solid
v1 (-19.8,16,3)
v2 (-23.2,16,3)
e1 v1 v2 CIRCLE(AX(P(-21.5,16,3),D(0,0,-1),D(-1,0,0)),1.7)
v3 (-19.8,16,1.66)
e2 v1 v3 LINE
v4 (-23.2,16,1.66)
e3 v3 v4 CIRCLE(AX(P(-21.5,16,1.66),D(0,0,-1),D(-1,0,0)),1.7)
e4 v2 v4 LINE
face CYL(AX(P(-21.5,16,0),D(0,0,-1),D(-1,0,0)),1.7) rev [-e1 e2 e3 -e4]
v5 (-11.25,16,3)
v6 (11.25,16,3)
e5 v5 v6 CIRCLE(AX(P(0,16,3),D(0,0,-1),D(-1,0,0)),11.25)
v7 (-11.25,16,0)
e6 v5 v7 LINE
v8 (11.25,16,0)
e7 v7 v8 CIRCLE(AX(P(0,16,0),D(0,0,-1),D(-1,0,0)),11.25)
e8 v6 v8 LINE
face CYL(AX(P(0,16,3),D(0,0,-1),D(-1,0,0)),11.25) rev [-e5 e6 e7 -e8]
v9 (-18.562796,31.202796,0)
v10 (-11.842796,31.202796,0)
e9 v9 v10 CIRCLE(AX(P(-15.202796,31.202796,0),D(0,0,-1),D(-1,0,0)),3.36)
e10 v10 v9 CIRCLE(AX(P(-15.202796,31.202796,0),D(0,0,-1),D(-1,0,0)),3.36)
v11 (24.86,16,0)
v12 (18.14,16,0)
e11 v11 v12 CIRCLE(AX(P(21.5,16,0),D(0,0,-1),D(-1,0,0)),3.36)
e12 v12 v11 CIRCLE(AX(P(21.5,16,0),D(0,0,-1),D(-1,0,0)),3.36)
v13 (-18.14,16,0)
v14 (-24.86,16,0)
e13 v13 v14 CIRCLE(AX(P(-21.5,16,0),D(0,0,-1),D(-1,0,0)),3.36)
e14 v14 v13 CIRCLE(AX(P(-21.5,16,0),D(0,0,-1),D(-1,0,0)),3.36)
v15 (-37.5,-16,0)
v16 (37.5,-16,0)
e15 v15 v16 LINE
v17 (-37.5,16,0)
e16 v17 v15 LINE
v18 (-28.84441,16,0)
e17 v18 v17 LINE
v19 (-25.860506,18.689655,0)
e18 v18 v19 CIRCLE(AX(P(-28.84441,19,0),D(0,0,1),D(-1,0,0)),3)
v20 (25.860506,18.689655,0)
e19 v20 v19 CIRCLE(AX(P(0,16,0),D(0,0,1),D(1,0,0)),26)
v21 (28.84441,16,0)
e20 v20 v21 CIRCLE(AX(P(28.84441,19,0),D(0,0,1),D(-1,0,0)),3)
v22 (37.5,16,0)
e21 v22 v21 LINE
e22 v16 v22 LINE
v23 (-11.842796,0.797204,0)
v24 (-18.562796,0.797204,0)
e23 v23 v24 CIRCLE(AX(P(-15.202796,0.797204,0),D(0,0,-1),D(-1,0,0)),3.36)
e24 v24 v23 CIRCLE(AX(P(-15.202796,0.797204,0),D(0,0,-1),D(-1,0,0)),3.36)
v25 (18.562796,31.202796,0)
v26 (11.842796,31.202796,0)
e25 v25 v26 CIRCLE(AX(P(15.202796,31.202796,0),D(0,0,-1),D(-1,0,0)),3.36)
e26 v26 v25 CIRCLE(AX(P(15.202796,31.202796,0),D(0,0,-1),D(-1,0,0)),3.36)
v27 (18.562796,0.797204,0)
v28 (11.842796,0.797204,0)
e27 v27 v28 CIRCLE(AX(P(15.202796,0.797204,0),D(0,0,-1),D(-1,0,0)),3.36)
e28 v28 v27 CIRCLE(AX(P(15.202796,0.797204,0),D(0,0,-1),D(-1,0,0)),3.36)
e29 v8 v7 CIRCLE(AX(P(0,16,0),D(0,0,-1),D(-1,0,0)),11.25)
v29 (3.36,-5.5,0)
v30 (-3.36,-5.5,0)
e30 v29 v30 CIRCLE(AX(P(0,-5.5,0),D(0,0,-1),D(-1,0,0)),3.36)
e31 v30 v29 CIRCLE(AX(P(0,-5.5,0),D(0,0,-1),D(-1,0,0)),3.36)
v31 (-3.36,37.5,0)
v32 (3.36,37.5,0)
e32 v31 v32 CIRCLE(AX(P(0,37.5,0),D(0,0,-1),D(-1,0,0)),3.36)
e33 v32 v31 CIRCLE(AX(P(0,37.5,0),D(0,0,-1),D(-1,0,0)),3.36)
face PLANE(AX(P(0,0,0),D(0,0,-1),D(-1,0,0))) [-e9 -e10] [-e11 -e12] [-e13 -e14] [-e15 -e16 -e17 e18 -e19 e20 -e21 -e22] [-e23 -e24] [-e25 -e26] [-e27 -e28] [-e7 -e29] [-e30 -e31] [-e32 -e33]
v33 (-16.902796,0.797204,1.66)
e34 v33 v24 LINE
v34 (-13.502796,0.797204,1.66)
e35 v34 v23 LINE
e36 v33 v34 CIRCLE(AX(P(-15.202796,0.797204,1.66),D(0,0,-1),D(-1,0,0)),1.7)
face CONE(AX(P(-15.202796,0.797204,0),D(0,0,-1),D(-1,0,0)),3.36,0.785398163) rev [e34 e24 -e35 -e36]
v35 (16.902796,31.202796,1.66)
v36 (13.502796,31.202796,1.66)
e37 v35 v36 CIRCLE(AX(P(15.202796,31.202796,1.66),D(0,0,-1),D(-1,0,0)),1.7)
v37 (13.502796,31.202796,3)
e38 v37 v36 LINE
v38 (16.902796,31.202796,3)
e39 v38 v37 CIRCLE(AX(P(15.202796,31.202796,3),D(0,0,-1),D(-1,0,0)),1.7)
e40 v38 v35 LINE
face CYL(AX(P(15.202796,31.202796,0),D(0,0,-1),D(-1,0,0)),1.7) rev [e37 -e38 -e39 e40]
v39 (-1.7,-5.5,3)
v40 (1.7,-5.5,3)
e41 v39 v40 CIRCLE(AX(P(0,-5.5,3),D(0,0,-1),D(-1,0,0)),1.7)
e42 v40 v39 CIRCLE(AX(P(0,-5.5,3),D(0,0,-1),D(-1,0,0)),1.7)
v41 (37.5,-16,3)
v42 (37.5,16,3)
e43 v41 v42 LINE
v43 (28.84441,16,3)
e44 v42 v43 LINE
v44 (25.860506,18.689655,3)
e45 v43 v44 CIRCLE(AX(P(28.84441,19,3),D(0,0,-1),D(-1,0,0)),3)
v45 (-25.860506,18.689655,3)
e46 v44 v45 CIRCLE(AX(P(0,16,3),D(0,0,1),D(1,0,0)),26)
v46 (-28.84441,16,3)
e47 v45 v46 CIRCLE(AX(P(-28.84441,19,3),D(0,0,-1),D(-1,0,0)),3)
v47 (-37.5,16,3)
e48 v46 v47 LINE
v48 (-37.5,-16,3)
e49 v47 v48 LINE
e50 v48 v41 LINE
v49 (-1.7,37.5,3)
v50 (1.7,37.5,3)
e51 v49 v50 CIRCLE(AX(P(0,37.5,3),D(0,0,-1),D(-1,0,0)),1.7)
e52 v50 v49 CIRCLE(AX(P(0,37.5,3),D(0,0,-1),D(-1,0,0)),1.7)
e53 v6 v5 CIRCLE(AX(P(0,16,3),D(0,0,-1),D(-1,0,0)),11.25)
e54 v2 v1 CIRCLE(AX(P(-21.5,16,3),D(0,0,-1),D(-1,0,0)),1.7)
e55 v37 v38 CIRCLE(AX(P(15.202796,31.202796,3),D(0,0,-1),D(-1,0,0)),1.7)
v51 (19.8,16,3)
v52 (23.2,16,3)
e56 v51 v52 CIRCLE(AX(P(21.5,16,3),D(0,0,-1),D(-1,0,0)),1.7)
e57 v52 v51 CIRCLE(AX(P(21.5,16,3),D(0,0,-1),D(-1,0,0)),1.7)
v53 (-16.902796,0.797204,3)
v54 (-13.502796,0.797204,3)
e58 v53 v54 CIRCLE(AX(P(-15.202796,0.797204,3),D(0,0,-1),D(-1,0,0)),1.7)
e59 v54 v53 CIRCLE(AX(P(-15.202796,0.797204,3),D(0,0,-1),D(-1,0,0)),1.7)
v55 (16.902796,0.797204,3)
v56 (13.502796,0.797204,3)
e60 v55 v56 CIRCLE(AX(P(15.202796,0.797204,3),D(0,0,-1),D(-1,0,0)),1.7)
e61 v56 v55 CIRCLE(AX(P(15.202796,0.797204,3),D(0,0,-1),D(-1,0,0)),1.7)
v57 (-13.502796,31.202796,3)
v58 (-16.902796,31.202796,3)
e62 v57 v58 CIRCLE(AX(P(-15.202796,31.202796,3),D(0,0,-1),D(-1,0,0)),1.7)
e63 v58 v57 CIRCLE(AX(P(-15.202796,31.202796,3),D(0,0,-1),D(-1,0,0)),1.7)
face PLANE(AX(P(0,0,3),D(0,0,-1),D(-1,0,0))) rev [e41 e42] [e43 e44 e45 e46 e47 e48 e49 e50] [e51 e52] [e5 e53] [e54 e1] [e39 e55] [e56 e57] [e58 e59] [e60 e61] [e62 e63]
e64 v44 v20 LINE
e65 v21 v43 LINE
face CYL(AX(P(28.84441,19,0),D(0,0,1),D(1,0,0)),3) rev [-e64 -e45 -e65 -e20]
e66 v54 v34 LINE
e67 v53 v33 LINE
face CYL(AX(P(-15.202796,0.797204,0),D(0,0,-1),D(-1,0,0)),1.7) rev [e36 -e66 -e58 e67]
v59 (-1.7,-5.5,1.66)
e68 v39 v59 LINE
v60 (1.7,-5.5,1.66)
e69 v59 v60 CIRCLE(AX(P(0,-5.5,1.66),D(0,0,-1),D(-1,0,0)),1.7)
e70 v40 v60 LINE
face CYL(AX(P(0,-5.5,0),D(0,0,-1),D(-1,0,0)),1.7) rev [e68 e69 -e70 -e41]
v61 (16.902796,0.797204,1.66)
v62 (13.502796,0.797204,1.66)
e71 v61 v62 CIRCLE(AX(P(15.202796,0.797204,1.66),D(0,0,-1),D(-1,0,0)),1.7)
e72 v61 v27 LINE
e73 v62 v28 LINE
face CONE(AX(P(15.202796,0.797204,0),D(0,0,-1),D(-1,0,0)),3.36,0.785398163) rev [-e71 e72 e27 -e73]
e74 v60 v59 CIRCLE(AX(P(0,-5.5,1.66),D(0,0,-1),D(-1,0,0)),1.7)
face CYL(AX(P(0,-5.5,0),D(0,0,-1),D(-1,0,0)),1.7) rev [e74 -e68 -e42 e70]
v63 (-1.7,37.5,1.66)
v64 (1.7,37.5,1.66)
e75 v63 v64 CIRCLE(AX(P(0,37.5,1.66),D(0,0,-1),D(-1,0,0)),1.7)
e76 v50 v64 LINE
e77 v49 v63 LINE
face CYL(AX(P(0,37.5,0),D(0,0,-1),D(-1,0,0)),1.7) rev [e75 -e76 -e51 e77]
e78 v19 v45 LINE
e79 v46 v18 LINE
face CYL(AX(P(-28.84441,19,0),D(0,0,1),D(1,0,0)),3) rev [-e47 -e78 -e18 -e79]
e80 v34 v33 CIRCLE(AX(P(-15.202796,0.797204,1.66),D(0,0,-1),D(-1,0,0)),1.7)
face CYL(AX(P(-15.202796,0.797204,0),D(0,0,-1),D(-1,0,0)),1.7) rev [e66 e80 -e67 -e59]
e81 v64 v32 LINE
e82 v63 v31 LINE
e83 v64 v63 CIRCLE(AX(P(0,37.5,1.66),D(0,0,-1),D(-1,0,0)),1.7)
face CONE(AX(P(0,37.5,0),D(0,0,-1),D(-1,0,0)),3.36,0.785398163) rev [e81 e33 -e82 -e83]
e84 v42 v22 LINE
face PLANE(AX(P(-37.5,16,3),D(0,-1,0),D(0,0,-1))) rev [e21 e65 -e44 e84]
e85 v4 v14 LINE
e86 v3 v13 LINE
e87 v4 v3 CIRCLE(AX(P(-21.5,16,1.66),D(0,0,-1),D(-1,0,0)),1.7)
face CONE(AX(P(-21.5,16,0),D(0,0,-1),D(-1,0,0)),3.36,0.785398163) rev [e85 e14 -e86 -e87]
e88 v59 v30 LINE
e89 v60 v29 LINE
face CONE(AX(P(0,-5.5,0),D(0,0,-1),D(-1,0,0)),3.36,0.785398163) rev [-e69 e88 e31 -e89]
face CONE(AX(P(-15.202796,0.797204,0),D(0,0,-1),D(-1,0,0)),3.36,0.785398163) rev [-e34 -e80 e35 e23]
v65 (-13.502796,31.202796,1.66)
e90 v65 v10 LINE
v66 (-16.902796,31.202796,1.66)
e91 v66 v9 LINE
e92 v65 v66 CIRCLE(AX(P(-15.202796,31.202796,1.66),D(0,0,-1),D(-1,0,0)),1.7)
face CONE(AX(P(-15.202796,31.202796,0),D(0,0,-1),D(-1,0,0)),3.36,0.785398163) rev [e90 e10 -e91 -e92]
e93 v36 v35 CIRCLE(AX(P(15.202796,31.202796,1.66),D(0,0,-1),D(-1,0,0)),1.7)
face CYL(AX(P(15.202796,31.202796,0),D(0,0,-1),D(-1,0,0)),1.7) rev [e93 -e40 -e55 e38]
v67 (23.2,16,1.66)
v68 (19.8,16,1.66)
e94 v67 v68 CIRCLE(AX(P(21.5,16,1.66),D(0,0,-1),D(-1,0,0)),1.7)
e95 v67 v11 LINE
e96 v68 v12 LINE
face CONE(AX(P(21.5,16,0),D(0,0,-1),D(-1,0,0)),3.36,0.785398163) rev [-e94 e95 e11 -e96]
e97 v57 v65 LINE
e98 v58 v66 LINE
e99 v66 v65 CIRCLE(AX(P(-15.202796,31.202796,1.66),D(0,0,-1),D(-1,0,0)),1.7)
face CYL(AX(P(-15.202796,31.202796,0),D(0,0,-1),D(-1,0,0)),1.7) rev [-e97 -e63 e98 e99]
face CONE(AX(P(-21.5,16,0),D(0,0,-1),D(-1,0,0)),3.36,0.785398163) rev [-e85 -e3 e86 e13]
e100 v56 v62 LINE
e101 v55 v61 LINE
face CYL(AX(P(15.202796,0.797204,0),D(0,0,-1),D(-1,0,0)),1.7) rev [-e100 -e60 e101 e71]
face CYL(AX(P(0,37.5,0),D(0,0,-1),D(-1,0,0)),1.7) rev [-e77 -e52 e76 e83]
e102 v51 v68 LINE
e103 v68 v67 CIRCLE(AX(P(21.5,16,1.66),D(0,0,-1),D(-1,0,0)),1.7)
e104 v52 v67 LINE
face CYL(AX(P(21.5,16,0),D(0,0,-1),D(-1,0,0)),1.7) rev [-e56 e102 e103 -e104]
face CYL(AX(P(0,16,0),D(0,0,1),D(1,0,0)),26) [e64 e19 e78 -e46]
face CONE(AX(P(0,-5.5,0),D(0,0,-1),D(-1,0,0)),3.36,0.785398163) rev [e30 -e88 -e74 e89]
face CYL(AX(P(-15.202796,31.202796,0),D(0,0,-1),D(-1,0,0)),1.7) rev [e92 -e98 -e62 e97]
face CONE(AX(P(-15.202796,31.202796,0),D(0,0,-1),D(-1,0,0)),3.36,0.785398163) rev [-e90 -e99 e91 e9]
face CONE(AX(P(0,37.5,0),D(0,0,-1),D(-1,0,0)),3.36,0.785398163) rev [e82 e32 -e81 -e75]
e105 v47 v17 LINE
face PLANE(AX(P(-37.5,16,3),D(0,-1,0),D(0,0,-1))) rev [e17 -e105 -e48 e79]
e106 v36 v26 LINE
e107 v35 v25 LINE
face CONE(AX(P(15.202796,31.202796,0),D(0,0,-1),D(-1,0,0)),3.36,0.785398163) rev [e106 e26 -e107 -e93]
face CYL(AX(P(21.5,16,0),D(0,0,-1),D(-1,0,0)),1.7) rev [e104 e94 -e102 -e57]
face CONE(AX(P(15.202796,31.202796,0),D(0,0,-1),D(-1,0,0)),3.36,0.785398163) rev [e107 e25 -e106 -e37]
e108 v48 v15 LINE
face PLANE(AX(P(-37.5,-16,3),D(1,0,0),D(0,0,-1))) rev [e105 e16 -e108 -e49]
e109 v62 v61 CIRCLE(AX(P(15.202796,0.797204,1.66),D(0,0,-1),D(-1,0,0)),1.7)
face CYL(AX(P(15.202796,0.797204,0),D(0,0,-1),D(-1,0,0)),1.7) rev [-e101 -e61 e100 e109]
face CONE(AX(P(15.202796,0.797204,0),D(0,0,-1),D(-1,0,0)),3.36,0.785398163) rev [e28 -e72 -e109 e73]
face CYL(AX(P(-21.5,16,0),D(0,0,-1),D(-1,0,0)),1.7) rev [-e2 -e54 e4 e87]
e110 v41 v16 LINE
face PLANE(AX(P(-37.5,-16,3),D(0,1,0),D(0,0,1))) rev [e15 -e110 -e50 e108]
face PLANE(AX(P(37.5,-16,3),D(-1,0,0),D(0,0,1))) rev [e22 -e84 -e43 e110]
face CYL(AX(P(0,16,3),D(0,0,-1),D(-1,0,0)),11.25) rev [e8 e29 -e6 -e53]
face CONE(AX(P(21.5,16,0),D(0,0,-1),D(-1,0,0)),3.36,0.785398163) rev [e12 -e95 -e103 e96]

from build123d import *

# Parameters (mm, degrees)
SKETCH_1_W                  = 75
SKETCH_1_H                  = 32
EXTRUDE_1_DEPTH             = 3
SKETCH_2_R                  = 26
EXTRUDE_3_DEPTH             = 3
FILLET_1_R                  = 3
SKETCH_3_R                  = 11.25
CUT_EXTRUDE_1_DEPTH         = 57.384838388
HOLE_WIZARD_M3_1_AT_2_COUNT = 2
HOLE_WIZARD_M3_1_AT_2_PITCH = 16.455387592
HOLE_WIZARD_M3_1_AT_3_COUNT = 2
HOLE_WIZARD_M3_1_AT_3_PITCH = 30.405591591
HOLE_WIZARD_M3_1_AT_4_COUNT = 2
HOLE_WIZARD_M3_1_AT_4_PITCH = 39.726819898
HOLE_WIZARD_M3_1_AT_5_COUNT = 2
HOLE_WIZARD_M3_1_AT_5_PITCH = 43
HOLE_WIZARD_M3_1_AT_6_COUNT = 2
HOLE_WIZARD_M3_1_AT_6_PITCH = 39.726819898
HOLE_WIZARD_M3_1_AT_7_COUNT = 2
HOLE_WIZARD_M3_1_AT_7_PITCH = 30.405591591
HOLE_WIZARD_M3_1_AT_8_COUNT = 2
HOLE_WIZARD_M3_1_AT_8_PITCH = 16.455387592


with BuildPart() as part:
    # 草图1 → 凸台-拉伸1 (new body)
    with BuildSketch(Plane.XY):
        Rectangle(SKETCH_1_W, SKETCH_1_H)
    extrude(amount=EXTRUDE_1_DEPTH)

    # 草图2 → 凸台-拉伸3 (add, through all)
    with BuildSketch(Plane.XY.offset(3)):
        with Locations((0, 16)):
            Circle(SKETCH_2_R)
    extrude(amount=-EXTRUDE_3_DEPTH)

    # 圆角1
    fillet_1_edges = [part.edges().sort_by_distance(p)[0] for p in [
        (26, 16, 1.5),
        (-26, 16, 1.5),
    ]]
    fillet(fillet_1_edges, radius=FILLET_1_R)

    # 草图3 → 切除-拉伸1 (cut, through all)
    with BuildSketch(Plane(origin=(0, 0, 0), x_dir=(-1, 0, 0), z_dir=(0, 0, -1))):
        with Locations((0, 16)):
            Circle(SKETCH_3_R)
    extrude(amount=-CUT_EXTRUDE_1_DEPTH, mode=Mode.SUBTRACT)

    # 草图5 → M3 六角凹锥坑螺钉的锥形沉头孔1 (revolve, cut)
    with BuildSketch(Plane(origin=(0, 37.5, 0), x_dir=(0, 1, 0), z_dir=(1, 0, 0))):
        Polygon((0, 0), (0, 3), (1.7, 3), (1.7, 1.66), (3.36, 0), align=None)
    hole_wizard_m3_1 = revolve(axis=Axis((0, 37.5, -6.35), (0, 0, 1)), mode=Mode.SUBTRACT)

    # M3 六角凹锥坑螺钉的锥形沉头孔1 at 2: M3 六角凹锥坑螺钉的锥形沉头孔1 ×2
    with Locations(*[Vector(-0.9238795325112867, -0.38268343236508967, 0) * (i * HOLE_WIZARD_M3_1_AT_2_PITCH) for i in range(1, HOLE_WIZARD_M3_1_AT_2_COUNT)]):
        add(hole_wizard_m3_1, mode=Mode.SUBTRACT)

    # M3 六角凹锥坑螺钉的锥形沉头孔1 at 3: M3 六角凹锥坑螺钉的锥形沉头孔1 ×2
    with Locations(*[Vector(-0.7071067811865476, -0.7071067811865475, 0) * (i * HOLE_WIZARD_M3_1_AT_3_PITCH) for i in range(1, HOLE_WIZARD_M3_1_AT_3_COUNT)]):
        add(hole_wizard_m3_1, mode=Mode.SUBTRACT)

    # M3 六角凹锥坑螺钉的锥形沉头孔1 at 4: M3 六角凹锥坑螺钉的锥形沉头孔1 ×2
    with Locations(*[Vector(-0.38268343236508995, -0.9238795325112867, 0) * (i * HOLE_WIZARD_M3_1_AT_4_PITCH) for i in range(1, HOLE_WIZARD_M3_1_AT_4_COUNT)]):
        add(hole_wizard_m3_1, mode=Mode.SUBTRACT)

    # M3 六角凹锥坑螺钉的锥形沉头孔1 at 5: M3 六角凹锥坑螺钉的锥形沉头孔1 ×2
    with Locations(*[(0, -i * HOLE_WIZARD_M3_1_AT_5_PITCH, 0) for i in range(1, HOLE_WIZARD_M3_1_AT_5_COUNT)]):
        add(hole_wizard_m3_1, mode=Mode.SUBTRACT)

    # M3 六角凹锥坑螺钉的锥形沉头孔1 at 6: M3 六角凹锥坑螺钉的锥形沉头孔1 ×2
    with Locations(*[Vector(0.38268343236508967, -0.9238795325112868, 0) * (i * HOLE_WIZARD_M3_1_AT_6_PITCH) for i in range(1, HOLE_WIZARD_M3_1_AT_6_COUNT)]):
        add(hole_wizard_m3_1, mode=Mode.SUBTRACT)

    # M3 六角凹锥坑螺钉的锥形沉头孔1 at 7: M3 六角凹锥坑螺钉的锥形沉头孔1 ×2
    with Locations(*[Vector(0.7071067811865474, -0.7071067811865477, 0) * (i * HOLE_WIZARD_M3_1_AT_7_PITCH) for i in range(1, HOLE_WIZARD_M3_1_AT_7_COUNT)]):
        add(hole_wizard_m3_1, mode=Mode.SUBTRACT)

    # M3 六角凹锥坑螺钉的锥形沉头孔1 at 8: M3 六角凹锥坑螺钉的锥形沉头孔1 ×2
    with Locations(*[Vector(0.9238795325112868, -0.3826834323650898, 0) * (i * HOLE_WIZARD_M3_1_AT_8_PITCH) for i in range(1, HOLE_WIZARD_M3_1_AT_8_COUNT)]):
        add(hole_wizard_m3_1, mode=Mode.SUBTRACT)


solid = part.part
